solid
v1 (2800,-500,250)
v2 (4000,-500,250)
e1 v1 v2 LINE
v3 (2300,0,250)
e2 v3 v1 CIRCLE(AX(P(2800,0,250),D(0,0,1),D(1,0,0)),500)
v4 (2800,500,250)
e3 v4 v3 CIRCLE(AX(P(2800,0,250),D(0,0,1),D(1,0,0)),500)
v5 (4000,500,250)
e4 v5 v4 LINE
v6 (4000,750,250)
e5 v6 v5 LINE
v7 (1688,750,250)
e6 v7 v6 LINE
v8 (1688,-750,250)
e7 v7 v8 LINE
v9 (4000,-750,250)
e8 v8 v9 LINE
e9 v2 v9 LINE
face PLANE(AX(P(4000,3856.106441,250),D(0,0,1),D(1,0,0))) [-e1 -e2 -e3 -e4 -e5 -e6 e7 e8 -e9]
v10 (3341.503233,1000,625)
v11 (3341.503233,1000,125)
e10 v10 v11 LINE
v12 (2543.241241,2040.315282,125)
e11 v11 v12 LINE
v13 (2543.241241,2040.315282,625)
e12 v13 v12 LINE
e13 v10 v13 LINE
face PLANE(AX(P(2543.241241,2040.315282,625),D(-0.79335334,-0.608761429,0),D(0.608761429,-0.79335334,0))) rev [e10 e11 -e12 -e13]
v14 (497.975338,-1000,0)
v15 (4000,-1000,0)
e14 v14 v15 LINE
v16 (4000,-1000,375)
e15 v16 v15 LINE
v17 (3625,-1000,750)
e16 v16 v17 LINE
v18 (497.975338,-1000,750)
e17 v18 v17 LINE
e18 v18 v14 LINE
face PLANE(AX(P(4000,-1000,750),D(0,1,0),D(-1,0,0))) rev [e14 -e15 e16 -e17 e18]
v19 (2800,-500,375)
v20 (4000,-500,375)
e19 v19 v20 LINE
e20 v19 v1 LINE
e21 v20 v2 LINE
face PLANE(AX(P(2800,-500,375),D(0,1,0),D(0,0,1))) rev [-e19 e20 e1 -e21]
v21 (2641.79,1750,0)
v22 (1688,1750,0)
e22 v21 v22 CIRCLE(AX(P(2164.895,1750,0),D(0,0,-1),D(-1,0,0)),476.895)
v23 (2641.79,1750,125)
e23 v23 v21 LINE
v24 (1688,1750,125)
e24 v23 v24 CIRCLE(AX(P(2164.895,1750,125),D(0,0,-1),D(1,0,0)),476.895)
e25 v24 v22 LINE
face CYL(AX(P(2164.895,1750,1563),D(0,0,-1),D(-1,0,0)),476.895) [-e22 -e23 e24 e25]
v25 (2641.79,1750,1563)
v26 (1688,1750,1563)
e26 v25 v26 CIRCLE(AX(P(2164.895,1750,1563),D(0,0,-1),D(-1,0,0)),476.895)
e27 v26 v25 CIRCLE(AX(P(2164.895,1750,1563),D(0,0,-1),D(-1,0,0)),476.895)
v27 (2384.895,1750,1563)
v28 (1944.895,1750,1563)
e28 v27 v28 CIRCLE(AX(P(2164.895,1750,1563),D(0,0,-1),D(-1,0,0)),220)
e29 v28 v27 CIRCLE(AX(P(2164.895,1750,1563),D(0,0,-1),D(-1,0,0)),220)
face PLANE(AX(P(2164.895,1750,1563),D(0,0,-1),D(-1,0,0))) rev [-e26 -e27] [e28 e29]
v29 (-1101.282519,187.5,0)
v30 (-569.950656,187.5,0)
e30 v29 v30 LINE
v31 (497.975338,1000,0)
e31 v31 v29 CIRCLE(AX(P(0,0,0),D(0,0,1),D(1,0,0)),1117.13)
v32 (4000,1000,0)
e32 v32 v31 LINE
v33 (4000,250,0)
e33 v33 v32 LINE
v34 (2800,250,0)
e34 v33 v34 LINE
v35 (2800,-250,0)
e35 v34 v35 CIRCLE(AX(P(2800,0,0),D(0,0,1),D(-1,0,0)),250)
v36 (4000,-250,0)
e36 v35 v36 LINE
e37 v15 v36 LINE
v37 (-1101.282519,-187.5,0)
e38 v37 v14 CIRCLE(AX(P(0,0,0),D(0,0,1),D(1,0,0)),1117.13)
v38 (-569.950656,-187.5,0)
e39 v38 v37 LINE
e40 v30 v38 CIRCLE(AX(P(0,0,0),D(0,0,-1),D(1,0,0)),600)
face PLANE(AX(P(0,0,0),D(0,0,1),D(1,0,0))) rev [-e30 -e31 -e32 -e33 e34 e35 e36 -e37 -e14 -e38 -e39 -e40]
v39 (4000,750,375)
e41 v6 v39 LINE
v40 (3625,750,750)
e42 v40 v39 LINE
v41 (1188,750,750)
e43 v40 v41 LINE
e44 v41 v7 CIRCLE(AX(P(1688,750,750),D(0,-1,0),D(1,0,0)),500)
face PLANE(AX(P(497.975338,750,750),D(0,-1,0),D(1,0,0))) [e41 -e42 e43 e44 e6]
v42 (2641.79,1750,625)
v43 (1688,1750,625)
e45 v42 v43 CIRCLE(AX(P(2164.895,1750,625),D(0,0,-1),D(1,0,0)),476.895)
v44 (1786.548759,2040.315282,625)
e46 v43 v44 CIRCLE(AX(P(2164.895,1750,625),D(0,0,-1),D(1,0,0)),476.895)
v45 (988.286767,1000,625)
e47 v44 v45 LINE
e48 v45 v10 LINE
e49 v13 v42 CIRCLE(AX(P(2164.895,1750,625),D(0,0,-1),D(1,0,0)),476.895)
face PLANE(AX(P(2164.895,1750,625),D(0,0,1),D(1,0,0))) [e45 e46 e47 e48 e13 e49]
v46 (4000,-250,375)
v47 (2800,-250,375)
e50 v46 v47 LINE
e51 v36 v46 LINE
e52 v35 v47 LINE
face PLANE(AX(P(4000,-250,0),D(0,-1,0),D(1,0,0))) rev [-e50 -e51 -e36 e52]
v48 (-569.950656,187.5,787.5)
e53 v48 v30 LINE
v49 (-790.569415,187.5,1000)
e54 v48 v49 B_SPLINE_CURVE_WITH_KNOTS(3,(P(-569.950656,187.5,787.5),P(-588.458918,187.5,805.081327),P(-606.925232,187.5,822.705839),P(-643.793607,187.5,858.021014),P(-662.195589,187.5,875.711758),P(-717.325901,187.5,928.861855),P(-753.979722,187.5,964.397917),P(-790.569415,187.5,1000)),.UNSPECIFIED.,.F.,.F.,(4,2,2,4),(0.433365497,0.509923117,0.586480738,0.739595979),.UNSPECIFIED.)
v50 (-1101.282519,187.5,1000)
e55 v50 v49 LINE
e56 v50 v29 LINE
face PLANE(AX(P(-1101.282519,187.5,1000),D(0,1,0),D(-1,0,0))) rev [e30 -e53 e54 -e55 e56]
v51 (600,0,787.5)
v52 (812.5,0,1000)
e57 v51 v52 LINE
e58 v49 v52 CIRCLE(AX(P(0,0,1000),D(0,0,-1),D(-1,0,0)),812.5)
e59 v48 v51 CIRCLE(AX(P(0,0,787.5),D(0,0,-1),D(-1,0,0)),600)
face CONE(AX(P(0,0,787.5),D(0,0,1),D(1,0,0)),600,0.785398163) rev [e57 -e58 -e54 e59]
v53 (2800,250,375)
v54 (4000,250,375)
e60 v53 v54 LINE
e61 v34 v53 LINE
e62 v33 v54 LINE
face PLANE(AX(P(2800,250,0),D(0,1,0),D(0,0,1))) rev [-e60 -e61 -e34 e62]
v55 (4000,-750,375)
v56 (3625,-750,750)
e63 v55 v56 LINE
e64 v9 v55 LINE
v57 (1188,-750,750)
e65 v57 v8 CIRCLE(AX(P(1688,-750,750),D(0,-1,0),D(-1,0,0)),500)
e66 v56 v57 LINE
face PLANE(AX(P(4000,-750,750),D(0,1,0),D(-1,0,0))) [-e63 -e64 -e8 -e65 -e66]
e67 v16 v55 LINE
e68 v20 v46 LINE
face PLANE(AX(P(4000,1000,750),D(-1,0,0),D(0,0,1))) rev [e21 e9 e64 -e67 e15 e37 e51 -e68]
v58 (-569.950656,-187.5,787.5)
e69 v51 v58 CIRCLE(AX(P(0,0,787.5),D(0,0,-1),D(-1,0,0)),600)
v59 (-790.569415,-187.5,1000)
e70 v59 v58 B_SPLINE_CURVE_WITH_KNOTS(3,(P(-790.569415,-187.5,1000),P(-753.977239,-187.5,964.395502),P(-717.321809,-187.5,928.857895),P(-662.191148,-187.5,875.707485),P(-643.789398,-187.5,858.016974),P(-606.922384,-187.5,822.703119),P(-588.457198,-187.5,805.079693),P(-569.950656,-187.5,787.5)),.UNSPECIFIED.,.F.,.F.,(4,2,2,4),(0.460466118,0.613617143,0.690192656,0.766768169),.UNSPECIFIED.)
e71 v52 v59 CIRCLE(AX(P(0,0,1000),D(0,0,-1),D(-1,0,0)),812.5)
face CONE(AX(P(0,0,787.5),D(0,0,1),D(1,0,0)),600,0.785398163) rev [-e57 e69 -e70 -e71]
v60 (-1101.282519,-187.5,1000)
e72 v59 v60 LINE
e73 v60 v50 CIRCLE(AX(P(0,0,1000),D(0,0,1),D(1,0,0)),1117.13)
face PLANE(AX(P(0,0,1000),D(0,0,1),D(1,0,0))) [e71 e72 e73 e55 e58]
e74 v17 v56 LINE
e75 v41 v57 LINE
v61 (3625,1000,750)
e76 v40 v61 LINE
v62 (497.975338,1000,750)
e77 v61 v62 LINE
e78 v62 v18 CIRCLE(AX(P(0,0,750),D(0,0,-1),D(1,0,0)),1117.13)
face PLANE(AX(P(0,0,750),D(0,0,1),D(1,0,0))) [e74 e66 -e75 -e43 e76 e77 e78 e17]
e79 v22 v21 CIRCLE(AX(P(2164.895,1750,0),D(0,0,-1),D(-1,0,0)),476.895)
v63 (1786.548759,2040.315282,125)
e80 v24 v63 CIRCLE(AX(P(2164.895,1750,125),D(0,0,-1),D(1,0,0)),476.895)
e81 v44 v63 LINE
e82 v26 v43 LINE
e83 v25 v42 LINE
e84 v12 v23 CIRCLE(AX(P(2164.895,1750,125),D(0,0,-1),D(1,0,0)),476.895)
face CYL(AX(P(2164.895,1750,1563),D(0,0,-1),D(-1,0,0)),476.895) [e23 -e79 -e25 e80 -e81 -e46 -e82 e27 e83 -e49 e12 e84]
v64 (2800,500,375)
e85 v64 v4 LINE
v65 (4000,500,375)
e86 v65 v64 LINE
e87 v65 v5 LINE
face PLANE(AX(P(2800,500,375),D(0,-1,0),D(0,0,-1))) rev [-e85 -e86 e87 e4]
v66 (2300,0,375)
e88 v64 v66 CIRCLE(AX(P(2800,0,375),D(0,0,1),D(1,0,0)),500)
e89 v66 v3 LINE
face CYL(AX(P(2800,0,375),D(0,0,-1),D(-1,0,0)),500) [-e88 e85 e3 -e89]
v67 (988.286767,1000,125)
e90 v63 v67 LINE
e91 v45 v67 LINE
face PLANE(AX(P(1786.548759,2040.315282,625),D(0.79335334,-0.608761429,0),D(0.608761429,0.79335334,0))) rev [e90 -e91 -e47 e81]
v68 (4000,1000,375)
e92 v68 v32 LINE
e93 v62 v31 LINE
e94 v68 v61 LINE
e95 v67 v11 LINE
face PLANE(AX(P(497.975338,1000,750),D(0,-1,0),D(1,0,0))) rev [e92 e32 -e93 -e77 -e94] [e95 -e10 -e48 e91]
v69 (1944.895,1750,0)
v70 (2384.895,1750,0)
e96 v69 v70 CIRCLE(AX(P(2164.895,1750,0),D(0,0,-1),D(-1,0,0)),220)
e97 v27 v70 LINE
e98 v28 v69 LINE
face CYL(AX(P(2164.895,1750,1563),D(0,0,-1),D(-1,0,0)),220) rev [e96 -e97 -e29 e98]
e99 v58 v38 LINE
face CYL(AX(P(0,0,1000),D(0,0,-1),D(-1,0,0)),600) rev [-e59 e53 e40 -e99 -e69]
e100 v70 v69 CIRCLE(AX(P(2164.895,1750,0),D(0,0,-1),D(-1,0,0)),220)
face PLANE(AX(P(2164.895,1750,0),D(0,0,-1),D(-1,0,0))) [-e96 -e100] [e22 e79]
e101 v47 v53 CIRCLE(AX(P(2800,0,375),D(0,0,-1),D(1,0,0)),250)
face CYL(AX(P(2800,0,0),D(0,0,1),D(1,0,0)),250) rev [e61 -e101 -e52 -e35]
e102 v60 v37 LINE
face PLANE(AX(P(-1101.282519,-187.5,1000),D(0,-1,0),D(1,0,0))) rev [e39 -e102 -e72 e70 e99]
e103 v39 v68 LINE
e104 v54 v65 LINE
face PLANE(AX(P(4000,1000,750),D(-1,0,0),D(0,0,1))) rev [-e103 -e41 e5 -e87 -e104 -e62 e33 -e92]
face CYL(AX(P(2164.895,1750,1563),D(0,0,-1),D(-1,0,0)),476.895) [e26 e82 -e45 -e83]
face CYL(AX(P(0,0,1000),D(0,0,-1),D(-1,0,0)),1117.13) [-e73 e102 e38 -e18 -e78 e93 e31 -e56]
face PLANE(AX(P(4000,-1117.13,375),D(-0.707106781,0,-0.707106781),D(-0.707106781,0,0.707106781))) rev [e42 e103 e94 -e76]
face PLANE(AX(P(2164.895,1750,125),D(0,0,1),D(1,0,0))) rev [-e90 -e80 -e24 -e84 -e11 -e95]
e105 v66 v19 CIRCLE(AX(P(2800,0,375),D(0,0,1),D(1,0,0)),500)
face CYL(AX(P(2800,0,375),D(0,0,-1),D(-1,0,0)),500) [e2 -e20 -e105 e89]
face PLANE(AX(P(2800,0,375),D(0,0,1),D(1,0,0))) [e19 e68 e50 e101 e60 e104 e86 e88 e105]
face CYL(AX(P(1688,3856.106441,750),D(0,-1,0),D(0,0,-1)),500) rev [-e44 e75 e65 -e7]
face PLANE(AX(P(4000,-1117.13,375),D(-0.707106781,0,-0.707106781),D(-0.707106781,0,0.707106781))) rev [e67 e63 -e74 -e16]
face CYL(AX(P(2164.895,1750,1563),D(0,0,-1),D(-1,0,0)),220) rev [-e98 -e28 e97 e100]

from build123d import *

# Parameters (mm, degrees)
SPLIT_HUB_DEPTH          = 1000
ARM_PLATE_DEPTH          = 750
SIDE_GROOVE_1_DEPTH      = 750
SIDE_START               = -750
SIDE_GROOVE_2_DEPTH      = 750
SLOT_END_CUT_DEPTH       = 4635.893681294
CLEVIS_SLOT_DEPTH        = 4221.246371588
CLEVIS_START             = 125
CLEVIS_LIP_DEPTH         = 125
TRUNNION_BOSS_SKETCH_R   = 476.895
TRUNNION_BOSS_SKETCH_R_2 = 220
TRUNNION_BOSS_DEPTH      = 1563
GUSSET_DEPTH             = 500


with BuildPart() as part:
    # Hub Profile Sketch → Split Hub (new body)
    with BuildSketch(Plane.XY):
        with BuildLine():
            Line((-1101.282519111, 187.5), (-569.950655759, 187.5))
            ThreePointArc((-569.950655759, 187.5), (600, 0), (-569.950655759, -187.5))
            Line((-569.950655759, -187.5), (-1101.282519111, -187.5))
            ThreePointArc((-1101.282519111, -187.5), (1117.13, 0), (-1101.282519111, 187.5))
        make_face()
    extrude(amount=SPLIT_HUB_DEPTH)

    # Arm Plate Sketch → Arm Plate (add)
    with BuildSketch(Plane.XY):
        with BuildLine():
            Line((497.975337642, 1000), (4000, 1000))
            Line((4000, 1000), (4000, -1000))
            Line((4000, -1000), (497.975337642, -1000))
            ThreePointArc((497.975337642, -1000), (1117.13, 0), (497.975337642, 1000))
        make_face()
    extrude(amount=ARM_PLATE_DEPTH)

    # Side Groove Sketch → Side Groove 1 (cut)
    with BuildSketch(Plane(origin=(0, 0, 0), x_dir=(1, 0, 0), z_dir=(0, 1, 0))):
        with BuildLine():
            Line((4000, -250), (1688, -250))
            ThreePointArc((1688, -250), (1334.446609407, -396.446609407), (1188, -750))
            Line((1188, -750), (4000, -750))
            Line((4000, -750), (4000, -250))
        make_face()
    extrude(amount=SIDE_GROOVE_1_DEPTH, mode=Mode.SUBTRACT)

    # Sketch3_2 → Side Groove 2 (cut)
    with BuildSketch(Plane(origin=(0, 0, 0), x_dir=(1, 0, 0), z_dir=(0, 1, 0)).offset(SIDE_START)):
        with BuildLine():
            Line((4000, -250), (1688, -250))
            ThreePointArc((1688, -250), (1334.446609407, -396.446609407), (1188, -750))
            Line((1188, -750), (4000, -750))
            Line((4000, -750), (4000, -250))
        make_face()
    extrude(amount=SIDE_GROOVE_2_DEPTH, mode=Mode.SUBTRACT)

    # Slot End Sketch → Slot End Cut (cut, through all)
    with BuildSketch(Plane(origin=(0, 1000, 0), x_dir=(1, 0, 0), z_dir=(0, 1, 0))):
        Polygon((4000, -375), (3625, -750), (4000, -750), align=None)
    extrude(amount=-SLOT_END_CUT_DEPTH, mode=Mode.SUBTRACT)

    # Clevis Slot Sketch → Clevis Slot (cut, through all)
    with BuildSketch(Plane.XY.offset(250)):
        with BuildLine():
            Line((2800, 250), (4000, 250))
            Line((4000, 250), (4000, -250))
            Line((4000, -250), (2800, -250))
            ThreePointArc((2800, -250), (2550, 0), (2800, 250))
        make_face()
    extrude(amount=-CLEVIS_SLOT_DEPTH, mode=Mode.SUBTRACT)

    # Clevis Lip Sketch → Clevis Lip (add)
    with BuildSketch(Plane.XY.offset(250).offset(CLEVIS_START)):
        with BuildLine():
            Line((2800, -250), (4000, -250))
            Line((4000, -250), (4000, -500))
            Line((4000, -500), (2800, -500))
            ThreePointArc((2800, -500), (2300, 0), (2800, 500))
            Line((2800, 500), (4000, 500))
            Line((4000, 500), (4000, 250))
            Line((4000, 250), (2800, 250))
            ThreePointArc((2800, 250), (2550, 0), (2800, -250))
        make_face()
    extrude(amount=-CLEVIS_LIP_DEPTH)



with BuildPart() as body_2:
    # Trunnion Boss Sketch → Trunnion Boss (new body)
    with BuildSketch(Plane(origin=(0, 0, 0), x_dir=(-1, 0, 0), z_dir=(0, 0, -1))):
        with Locations((-2164.895, 1750)):
            Circle(TRUNNION_BOSS_SKETCH_R)
        with Locations((-2164.895, 1750)):
            Circle(TRUNNION_BOSS_SKETCH_R_2, mode=Mode.SUBTRACT)
    extrude(amount=-TRUNNION_BOSS_DEPTH)


with BuildPart() as part_1:
    add(part.part)

    add(body_2.part)  # Gusset merges body 2
    # Gusset Sketch → Gusset (add)
    with BuildSketch(Plane.XY.offset(125)):
        with BuildLine():
            Line((2543.241241218, 2040.315281687), (3341.503232864, 1000))
            Line((3341.503232864, 1000), (988.286767136, 1000))
            Line((988.286767136, 1000), (1786.548758782, 2040.315281687))
            ThreePointArc((1786.548758782, 2040.315281687), (2164.895, 1273.105), (2543.241241218, 2040.315281687))
        make_face()
    extrude(amount=GUSSET_DEPTH)

    # Revolved Cut Sketch → Revolved Relief Cut (revolve, cut)
    with BuildSketch(Plane(origin=(0, 0, 0), x_dir=(0, 0, -1), z_dir=(1, 0, 0))):
        Polygon((0, 600), (-787.5, 600), (-1000, 812.5), (-1000, 0), (0, 0), align=None)
    revolve(axis=Axis((0, 0, 0), (0, 0, 1)), mode=Mode.SUBTRACT)


solid = part_1.part
